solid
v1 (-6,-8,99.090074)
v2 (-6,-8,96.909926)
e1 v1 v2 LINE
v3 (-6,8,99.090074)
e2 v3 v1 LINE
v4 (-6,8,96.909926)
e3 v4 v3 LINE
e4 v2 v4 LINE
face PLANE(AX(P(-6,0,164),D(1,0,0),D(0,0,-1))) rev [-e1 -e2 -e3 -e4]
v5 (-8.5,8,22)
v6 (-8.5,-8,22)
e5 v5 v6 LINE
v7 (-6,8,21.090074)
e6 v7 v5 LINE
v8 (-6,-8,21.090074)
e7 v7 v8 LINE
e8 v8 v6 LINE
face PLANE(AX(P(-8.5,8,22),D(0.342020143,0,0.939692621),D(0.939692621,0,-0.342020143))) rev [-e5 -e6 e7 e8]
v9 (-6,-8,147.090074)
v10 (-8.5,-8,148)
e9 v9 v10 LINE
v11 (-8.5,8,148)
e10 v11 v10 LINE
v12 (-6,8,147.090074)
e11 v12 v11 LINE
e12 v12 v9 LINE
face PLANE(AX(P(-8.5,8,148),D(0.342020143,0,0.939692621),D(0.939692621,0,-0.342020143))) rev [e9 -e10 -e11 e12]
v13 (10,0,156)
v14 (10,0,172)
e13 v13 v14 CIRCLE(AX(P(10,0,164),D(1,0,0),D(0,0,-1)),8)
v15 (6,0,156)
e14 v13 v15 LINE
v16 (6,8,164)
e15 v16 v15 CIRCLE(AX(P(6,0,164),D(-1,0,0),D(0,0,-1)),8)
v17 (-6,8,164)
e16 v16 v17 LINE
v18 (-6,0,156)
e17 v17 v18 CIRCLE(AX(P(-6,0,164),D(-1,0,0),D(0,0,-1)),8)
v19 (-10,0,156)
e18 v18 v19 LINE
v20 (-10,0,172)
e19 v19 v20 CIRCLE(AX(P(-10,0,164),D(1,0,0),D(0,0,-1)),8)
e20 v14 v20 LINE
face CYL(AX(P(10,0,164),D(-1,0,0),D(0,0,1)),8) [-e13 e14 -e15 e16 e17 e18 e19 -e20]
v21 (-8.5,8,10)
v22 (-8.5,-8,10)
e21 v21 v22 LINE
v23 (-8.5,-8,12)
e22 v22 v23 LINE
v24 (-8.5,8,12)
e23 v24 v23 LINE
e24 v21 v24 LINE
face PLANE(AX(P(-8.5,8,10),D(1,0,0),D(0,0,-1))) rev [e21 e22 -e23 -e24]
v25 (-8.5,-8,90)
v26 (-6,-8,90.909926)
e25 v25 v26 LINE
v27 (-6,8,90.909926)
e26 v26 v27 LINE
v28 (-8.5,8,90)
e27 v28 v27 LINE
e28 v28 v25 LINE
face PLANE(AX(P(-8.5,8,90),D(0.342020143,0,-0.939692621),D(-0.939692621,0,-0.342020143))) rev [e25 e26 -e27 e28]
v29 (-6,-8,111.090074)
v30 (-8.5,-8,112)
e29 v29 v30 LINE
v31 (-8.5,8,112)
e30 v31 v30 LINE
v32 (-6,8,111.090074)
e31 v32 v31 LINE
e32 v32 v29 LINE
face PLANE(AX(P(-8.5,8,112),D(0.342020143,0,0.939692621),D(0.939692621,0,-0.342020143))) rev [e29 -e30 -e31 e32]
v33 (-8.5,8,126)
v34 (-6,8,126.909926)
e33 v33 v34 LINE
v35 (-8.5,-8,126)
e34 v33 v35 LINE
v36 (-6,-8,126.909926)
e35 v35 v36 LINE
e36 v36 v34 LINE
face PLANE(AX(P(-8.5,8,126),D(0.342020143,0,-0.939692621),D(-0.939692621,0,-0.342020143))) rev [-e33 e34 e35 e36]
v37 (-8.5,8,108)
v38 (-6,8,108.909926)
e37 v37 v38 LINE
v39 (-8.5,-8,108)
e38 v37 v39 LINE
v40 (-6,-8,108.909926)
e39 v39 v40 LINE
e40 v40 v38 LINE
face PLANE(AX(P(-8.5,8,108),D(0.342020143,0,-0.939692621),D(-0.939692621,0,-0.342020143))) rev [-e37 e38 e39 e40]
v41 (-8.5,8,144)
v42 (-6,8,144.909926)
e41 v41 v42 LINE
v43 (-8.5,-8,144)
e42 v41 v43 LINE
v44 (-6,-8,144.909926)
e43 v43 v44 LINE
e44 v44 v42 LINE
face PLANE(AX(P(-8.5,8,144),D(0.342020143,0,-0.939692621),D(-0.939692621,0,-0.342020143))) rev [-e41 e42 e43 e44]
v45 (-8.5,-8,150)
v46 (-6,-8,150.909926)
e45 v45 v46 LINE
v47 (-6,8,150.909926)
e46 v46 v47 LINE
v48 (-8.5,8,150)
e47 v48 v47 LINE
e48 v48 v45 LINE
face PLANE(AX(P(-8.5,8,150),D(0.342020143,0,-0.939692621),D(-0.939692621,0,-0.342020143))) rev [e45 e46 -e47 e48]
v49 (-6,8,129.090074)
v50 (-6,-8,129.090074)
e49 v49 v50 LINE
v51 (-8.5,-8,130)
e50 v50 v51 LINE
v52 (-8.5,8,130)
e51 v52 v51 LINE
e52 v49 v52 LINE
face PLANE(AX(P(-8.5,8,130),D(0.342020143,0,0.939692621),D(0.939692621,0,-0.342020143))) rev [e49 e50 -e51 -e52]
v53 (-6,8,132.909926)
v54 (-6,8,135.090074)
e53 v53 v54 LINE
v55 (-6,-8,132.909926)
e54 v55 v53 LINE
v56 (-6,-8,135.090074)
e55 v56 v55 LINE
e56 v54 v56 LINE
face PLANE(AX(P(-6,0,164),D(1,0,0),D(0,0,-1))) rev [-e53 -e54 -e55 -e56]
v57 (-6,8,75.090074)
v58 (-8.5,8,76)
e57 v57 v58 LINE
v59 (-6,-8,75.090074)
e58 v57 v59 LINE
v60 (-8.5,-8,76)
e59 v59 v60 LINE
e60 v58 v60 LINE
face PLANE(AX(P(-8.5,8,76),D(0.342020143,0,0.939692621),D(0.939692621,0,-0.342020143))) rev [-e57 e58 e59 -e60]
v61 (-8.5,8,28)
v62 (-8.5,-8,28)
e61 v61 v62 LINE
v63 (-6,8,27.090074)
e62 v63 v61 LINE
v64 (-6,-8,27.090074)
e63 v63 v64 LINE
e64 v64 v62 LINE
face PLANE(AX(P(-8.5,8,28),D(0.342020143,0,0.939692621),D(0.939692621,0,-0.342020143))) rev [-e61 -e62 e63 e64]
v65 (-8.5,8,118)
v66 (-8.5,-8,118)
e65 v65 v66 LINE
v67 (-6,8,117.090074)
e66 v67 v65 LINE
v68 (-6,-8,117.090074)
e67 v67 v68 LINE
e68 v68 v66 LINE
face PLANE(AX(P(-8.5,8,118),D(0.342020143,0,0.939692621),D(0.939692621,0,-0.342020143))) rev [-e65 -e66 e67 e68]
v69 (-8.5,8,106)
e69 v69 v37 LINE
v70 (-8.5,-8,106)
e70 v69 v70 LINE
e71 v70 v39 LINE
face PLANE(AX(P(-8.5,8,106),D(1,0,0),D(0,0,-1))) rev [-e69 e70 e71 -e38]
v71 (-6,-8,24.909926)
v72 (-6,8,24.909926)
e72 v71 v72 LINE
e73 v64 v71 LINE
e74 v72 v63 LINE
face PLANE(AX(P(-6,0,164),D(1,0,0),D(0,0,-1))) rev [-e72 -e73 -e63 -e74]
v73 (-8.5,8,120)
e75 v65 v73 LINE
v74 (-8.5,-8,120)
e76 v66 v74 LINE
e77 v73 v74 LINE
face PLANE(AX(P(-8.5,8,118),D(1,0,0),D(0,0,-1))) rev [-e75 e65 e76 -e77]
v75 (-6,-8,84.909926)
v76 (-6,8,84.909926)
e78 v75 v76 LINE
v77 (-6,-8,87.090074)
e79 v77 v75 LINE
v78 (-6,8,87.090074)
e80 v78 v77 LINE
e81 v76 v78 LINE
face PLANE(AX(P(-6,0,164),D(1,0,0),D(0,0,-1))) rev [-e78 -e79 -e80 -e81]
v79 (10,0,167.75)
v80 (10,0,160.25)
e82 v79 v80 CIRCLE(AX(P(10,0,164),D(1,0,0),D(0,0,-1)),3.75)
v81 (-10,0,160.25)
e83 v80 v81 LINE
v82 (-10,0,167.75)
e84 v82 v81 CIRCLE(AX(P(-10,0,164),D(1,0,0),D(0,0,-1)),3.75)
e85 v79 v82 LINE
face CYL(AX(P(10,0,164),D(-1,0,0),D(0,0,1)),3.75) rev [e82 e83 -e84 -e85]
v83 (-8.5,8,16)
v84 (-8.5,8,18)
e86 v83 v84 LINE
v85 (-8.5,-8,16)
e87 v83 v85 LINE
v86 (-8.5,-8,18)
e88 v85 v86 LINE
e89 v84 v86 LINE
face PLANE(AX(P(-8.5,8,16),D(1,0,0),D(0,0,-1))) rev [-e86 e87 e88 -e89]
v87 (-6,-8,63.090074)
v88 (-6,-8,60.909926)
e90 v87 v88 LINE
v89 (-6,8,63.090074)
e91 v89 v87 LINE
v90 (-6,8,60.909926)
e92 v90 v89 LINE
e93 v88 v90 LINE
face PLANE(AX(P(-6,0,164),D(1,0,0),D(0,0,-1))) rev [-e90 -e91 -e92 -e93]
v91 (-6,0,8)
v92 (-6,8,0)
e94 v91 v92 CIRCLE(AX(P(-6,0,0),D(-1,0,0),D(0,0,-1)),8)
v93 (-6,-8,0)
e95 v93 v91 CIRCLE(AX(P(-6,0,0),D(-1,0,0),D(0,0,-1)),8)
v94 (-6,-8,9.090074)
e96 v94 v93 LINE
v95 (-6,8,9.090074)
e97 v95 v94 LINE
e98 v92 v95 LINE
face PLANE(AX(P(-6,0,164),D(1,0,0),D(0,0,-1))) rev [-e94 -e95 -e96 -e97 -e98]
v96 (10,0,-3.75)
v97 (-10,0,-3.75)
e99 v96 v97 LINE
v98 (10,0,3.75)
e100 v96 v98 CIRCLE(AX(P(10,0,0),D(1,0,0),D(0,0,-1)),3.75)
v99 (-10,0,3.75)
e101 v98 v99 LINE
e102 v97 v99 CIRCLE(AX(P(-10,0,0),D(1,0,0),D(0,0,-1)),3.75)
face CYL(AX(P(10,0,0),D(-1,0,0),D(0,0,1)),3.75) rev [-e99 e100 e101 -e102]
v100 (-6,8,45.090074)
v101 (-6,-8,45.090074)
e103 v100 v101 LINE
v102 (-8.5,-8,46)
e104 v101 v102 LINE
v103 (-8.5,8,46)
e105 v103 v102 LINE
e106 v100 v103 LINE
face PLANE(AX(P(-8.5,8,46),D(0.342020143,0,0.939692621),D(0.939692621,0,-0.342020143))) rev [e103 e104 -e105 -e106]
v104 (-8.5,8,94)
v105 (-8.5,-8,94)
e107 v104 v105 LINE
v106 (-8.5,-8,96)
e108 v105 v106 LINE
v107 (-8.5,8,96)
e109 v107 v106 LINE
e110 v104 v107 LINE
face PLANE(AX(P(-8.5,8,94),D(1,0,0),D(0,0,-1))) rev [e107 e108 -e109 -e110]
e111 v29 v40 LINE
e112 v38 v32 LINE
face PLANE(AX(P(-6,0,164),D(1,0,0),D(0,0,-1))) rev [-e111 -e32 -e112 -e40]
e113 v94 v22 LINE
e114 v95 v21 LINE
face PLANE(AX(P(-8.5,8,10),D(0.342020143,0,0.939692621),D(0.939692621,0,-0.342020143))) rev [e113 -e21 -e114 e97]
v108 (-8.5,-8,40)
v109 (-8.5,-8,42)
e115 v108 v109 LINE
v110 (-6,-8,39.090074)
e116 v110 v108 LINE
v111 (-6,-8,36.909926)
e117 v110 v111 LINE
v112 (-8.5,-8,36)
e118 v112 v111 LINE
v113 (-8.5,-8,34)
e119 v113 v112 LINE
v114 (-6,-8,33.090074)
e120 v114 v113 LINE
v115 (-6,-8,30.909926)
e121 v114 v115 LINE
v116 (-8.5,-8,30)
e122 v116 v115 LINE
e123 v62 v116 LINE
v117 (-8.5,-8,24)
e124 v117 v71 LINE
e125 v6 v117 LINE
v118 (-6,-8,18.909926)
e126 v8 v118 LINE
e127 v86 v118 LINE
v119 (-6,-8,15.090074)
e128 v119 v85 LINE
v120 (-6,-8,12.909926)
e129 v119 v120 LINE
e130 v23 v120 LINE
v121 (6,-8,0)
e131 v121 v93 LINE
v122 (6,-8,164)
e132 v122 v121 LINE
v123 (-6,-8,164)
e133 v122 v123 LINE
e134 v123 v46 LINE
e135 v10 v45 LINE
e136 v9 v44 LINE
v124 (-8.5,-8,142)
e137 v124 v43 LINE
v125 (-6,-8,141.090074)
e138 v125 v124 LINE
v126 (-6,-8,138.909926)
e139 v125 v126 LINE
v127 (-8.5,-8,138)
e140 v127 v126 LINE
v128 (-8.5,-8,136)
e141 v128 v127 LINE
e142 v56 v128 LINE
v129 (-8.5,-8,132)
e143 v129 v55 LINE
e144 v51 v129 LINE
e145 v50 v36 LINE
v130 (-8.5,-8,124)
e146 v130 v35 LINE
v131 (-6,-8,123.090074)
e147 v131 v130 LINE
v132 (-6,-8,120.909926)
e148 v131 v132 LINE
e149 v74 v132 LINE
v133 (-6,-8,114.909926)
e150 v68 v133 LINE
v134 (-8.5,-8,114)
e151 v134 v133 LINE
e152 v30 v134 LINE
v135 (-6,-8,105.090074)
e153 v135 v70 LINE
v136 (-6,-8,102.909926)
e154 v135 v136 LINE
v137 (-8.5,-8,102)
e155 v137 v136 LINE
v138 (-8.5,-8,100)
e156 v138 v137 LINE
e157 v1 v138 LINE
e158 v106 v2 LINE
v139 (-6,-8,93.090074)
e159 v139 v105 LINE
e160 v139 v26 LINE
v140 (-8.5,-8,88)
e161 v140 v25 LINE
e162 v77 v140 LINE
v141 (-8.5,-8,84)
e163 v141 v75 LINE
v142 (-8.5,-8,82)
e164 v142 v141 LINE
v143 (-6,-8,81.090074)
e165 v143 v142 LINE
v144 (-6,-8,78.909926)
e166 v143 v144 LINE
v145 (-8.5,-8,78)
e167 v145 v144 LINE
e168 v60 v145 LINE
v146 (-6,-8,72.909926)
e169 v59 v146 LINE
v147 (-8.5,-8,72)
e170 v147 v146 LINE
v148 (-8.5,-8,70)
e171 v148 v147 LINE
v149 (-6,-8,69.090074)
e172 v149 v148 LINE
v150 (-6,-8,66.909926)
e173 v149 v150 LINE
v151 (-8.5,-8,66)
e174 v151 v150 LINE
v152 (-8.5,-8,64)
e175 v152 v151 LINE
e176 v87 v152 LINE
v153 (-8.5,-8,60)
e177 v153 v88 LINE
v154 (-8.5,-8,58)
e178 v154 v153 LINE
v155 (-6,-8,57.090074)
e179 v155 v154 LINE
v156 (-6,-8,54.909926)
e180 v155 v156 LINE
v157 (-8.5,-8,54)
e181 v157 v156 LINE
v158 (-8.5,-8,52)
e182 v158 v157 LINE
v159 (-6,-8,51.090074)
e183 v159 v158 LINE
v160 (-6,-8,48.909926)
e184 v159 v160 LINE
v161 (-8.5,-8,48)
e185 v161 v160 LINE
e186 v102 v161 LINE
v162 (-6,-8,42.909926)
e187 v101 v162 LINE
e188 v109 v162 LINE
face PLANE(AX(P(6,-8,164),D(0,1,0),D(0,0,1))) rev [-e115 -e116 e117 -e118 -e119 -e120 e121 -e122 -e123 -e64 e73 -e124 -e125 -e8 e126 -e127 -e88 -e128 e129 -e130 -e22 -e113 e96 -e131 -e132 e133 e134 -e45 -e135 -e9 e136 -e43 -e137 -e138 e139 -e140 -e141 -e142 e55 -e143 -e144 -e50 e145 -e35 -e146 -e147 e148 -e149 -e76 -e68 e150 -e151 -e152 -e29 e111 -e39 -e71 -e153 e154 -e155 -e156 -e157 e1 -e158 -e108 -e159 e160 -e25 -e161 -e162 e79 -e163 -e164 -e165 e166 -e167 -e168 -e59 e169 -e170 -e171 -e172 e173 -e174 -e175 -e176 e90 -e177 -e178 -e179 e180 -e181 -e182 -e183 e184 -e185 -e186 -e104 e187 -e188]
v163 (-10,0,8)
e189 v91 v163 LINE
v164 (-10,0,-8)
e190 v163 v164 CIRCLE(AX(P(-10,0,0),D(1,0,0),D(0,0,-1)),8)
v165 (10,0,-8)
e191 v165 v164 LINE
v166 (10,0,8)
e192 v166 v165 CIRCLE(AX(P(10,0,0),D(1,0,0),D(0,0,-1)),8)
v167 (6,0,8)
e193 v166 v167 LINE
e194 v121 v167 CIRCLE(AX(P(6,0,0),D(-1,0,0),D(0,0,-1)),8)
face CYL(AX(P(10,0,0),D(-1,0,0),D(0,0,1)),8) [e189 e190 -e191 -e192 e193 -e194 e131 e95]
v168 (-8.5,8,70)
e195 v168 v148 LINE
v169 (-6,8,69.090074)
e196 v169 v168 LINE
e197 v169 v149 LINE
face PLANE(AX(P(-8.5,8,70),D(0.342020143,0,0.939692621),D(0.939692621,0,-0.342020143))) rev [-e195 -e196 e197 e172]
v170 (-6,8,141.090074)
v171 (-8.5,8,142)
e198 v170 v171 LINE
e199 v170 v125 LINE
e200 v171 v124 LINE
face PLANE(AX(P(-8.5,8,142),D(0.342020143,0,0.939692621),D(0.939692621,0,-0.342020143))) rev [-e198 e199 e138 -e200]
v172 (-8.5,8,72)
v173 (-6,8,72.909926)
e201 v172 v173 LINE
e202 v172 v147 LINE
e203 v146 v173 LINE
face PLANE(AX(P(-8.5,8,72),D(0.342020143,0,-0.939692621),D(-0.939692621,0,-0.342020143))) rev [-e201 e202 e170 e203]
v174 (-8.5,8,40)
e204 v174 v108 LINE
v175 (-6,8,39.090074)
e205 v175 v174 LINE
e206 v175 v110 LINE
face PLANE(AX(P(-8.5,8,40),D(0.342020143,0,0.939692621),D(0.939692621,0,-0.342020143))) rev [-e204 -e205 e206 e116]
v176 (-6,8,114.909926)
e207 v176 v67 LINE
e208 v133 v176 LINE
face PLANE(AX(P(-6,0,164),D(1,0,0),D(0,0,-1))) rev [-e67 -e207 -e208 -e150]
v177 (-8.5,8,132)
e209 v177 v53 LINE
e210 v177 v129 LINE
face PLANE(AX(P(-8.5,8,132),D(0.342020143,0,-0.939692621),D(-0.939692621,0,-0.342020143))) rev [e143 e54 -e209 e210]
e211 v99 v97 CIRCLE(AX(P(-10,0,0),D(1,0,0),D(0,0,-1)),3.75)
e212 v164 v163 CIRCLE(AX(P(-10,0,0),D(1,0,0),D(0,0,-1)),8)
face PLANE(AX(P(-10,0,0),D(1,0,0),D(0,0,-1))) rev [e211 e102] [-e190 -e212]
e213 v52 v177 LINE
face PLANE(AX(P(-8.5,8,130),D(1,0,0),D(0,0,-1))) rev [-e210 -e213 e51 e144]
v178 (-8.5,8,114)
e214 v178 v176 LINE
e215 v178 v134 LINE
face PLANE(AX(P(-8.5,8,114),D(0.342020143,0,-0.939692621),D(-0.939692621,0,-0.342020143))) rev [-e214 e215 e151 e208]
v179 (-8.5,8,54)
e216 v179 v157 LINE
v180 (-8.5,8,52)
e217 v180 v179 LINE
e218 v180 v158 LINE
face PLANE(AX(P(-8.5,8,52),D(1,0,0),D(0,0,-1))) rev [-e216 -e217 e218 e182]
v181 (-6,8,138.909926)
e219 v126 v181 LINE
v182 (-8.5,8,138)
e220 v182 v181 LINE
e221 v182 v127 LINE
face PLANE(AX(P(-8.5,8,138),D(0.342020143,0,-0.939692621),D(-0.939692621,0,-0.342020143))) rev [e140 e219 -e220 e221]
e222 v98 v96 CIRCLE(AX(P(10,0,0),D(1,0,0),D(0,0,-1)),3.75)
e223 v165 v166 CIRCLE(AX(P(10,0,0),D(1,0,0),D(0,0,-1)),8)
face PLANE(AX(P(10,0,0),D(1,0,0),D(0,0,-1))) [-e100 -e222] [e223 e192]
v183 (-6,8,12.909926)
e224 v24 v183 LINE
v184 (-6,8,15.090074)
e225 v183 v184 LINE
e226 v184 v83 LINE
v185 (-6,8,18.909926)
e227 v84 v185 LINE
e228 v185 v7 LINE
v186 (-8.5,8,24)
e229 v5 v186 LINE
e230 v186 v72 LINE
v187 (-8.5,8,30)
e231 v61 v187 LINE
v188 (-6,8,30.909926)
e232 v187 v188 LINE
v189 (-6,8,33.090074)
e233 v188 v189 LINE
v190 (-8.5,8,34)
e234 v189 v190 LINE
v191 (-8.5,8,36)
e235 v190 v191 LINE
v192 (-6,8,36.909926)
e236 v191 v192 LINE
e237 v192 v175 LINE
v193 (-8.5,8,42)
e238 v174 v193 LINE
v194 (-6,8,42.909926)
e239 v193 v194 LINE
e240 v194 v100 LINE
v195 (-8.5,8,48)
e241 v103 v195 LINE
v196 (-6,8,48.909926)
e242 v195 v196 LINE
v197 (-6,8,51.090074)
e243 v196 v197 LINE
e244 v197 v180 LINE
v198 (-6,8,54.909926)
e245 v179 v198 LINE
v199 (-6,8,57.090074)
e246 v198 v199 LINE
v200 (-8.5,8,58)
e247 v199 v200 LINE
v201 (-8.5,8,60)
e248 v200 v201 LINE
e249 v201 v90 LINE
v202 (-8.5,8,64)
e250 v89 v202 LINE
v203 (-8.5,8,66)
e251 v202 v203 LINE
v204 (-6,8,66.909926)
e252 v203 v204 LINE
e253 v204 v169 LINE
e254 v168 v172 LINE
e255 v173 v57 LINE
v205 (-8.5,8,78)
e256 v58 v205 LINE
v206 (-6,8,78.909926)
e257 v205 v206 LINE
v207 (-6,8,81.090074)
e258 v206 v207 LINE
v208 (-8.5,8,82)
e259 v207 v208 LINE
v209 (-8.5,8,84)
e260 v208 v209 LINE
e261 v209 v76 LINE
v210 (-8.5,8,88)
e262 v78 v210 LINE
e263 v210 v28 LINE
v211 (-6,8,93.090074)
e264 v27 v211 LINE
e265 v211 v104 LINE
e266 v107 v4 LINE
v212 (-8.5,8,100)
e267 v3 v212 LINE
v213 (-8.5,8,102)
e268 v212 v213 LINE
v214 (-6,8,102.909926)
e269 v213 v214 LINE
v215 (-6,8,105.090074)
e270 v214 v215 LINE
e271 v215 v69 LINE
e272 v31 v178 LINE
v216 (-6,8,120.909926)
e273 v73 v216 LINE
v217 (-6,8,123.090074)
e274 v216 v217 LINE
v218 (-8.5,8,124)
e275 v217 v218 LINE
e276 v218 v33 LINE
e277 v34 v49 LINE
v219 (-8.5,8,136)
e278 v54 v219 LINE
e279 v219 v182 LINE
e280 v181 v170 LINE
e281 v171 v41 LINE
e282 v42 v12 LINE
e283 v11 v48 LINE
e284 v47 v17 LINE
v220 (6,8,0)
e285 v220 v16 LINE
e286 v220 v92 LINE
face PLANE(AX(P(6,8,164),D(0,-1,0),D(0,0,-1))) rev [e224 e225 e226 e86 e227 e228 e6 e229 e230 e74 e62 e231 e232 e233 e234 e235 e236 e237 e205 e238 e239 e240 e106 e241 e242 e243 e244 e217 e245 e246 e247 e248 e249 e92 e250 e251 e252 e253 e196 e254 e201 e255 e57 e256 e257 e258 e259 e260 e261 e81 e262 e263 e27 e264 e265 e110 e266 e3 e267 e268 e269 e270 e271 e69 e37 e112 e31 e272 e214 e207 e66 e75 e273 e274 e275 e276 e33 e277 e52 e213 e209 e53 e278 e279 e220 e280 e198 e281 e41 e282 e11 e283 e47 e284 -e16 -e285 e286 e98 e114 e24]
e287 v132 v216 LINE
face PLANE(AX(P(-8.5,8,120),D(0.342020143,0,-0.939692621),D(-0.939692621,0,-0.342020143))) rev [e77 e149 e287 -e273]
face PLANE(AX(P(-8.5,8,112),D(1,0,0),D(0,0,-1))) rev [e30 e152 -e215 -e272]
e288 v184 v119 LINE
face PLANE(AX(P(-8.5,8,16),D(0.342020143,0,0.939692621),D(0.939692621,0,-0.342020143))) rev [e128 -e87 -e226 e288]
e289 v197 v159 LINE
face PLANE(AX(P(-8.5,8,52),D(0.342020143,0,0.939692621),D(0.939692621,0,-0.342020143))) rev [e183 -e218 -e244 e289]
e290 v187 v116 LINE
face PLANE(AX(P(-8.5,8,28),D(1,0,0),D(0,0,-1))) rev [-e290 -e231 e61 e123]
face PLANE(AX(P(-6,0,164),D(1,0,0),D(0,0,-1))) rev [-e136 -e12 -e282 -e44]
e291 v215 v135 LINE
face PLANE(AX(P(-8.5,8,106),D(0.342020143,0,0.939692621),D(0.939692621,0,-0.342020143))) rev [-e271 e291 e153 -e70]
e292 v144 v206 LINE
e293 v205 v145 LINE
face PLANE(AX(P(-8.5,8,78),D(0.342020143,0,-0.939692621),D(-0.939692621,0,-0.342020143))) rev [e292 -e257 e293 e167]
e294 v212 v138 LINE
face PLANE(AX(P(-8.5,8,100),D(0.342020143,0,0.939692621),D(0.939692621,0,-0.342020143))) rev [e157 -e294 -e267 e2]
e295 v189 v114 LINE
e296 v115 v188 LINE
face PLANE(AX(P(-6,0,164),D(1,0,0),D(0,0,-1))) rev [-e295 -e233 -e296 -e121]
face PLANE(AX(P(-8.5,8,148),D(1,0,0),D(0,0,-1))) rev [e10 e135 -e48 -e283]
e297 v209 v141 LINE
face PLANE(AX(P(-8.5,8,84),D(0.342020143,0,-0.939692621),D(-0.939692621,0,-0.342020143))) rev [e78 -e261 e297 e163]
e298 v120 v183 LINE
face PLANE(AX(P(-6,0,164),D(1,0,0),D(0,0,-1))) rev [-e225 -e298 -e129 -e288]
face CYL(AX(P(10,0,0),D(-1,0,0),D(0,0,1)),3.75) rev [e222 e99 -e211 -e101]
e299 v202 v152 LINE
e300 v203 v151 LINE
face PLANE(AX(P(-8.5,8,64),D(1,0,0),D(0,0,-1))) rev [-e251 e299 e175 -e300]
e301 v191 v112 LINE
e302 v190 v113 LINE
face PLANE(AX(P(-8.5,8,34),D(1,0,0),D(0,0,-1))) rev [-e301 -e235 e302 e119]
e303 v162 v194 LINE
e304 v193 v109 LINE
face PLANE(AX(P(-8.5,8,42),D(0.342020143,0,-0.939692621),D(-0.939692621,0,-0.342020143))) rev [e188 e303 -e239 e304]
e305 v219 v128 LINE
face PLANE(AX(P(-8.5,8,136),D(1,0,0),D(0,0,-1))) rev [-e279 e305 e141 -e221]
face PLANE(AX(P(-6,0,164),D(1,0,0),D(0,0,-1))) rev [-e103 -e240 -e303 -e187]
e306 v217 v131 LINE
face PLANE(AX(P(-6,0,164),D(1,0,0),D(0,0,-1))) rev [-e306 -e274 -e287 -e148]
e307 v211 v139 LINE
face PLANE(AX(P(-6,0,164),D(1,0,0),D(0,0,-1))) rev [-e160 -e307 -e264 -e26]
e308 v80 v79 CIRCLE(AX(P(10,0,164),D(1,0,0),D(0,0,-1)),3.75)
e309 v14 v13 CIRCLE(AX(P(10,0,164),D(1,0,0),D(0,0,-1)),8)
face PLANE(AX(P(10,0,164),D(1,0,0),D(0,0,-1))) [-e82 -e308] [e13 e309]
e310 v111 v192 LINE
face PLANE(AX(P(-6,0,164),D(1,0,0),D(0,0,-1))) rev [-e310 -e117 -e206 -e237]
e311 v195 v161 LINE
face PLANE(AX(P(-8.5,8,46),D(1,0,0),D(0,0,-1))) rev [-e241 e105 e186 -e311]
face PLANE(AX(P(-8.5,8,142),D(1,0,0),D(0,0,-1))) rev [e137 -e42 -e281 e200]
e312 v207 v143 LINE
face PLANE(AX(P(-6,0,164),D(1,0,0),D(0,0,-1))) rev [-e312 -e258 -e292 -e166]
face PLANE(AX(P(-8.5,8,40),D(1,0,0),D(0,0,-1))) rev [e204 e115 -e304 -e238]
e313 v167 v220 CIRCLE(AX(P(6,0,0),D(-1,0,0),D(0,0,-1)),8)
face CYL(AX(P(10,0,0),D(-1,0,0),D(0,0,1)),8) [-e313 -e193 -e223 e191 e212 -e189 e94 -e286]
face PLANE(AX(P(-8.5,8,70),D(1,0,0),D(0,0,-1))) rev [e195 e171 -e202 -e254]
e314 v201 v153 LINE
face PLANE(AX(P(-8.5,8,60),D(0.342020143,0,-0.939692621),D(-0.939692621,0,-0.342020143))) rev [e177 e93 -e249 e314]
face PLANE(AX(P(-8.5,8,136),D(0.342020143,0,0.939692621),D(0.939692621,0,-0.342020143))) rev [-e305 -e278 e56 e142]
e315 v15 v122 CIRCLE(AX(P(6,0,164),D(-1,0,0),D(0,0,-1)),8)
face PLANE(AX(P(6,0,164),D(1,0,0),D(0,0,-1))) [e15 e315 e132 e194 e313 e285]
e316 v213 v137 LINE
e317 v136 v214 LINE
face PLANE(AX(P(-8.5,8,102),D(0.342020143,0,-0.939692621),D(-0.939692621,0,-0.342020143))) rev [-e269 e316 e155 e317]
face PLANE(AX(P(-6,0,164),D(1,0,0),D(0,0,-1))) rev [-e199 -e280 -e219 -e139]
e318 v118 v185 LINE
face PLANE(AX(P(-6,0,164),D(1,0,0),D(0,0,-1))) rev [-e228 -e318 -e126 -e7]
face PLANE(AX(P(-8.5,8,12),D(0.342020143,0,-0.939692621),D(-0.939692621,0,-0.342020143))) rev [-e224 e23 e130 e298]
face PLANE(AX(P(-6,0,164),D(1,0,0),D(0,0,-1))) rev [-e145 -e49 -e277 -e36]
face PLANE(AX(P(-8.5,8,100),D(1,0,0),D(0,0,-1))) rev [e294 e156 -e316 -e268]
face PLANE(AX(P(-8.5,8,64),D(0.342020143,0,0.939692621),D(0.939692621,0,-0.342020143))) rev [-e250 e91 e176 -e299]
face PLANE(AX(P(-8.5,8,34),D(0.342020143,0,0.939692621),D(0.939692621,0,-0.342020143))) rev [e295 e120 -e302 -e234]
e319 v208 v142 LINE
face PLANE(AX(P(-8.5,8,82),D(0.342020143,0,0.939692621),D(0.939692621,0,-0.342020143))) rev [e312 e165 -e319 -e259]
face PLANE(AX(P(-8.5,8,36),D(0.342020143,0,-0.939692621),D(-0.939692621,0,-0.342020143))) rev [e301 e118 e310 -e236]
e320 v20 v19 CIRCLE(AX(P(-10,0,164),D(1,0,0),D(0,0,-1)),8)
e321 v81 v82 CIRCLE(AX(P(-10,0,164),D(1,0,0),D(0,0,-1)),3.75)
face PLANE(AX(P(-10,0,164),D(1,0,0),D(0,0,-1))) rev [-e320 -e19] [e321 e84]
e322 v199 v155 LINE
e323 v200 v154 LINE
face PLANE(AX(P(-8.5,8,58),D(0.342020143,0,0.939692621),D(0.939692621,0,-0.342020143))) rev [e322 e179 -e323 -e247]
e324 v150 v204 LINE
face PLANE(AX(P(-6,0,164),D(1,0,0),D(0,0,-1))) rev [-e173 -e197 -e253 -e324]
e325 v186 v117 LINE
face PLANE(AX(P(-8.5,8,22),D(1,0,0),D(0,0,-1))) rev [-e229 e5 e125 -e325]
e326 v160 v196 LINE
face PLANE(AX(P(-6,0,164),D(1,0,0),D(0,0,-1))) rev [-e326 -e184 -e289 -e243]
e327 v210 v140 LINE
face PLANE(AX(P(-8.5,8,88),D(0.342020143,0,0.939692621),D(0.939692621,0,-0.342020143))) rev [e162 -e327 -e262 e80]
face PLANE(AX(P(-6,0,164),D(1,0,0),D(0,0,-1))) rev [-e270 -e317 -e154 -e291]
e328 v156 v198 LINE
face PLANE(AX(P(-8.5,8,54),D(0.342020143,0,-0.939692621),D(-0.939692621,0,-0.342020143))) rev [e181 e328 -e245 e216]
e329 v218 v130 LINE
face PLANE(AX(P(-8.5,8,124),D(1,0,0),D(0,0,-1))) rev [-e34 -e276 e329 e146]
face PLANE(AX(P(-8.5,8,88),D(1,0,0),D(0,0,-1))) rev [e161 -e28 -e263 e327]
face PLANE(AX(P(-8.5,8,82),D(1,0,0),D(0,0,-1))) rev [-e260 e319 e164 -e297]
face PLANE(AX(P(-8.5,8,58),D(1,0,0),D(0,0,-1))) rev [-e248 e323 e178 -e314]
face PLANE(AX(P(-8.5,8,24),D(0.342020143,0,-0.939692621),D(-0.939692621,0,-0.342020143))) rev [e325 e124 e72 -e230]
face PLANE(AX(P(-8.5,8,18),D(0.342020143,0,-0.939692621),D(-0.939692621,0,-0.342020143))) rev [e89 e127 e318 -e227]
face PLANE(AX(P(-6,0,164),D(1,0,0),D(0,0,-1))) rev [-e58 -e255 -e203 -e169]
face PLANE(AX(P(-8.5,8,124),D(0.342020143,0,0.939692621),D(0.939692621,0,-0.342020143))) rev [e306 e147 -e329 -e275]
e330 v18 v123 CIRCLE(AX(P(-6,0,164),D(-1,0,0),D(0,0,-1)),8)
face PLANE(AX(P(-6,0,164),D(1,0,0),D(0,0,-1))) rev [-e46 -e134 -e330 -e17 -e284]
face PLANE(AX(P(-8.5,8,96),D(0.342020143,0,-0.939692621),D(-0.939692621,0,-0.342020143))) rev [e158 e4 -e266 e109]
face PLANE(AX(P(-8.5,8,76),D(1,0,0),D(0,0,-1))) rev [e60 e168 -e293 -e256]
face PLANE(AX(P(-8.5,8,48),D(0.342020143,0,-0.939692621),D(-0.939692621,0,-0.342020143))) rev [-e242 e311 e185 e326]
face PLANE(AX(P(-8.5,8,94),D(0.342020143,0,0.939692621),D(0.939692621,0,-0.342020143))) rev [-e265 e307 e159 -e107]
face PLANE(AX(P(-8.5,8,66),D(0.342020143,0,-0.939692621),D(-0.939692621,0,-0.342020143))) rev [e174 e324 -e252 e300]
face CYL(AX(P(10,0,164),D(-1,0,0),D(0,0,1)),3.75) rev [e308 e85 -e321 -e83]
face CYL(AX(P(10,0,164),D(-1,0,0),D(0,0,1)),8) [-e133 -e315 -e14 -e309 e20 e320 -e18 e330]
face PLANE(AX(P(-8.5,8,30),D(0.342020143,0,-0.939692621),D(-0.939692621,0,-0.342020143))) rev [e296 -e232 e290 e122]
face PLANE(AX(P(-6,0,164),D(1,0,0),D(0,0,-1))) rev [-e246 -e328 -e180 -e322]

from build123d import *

# Parameters (mm, degrees)
EYE_BAR_PROFILE_SKETCH_R   = 8
EYE_BAR_PROFILE_SKETCH_R_2 = 3.75
BAR_WITH_EYE_ENDS_DEPTH    = 10
BAR_WITH_EYE_ENDS_2_DEPTH  = 10
RACK_BODY_DEPTH            = 6
RACK_TEETH_24X_DEPTH       = 8


with BuildPart() as part:
    # Eye Bar Profile Sketch → Bar With Eye Ends (new, symmetric)
    with BuildSketch(Plane(origin=(0, 0, 0), x_dir=(0, 0, -1), z_dir=(1, 0, 0))):
        Circle(EYE_BAR_PROFILE_SKETCH_R)
        Circle(EYE_BAR_PROFILE_SKETCH_R_2, mode=Mode.SUBTRACT)
    extrude(amount=BAR_WITH_EYE_ENDS_DEPTH, both=True)



with BuildPart() as body_2:
    # Eye Bar Profile Sketch → Bar With Eye Ends 2 (new, symmetric)
    with BuildSketch(Plane(origin=(0, 0, 0), x_dir=(0, 0, -1), z_dir=(1, 0, 0))):
        with Locations((-164, 0)):
            Circle(EYE_BAR_PROFILE_SKETCH_R)
        with Locations((-164, 0)):
            Circle(EYE_BAR_PROFILE_SKETCH_R_2, mode=Mode.SUBTRACT)
    extrude(amount=BAR_WITH_EYE_ENDS_2_DEPTH, both=True)


with BuildPart() as part_1:
    add(part.part)

    add(body_2.part)  # Rack Body merges body 2
    # Rack Body Sketch → Rack Body (add, symmetric)
    with BuildSketch(Plane(origin=(0, 0, 0), x_dir=(0, 0, -1), z_dir=(1, 0, 0))):
        with BuildLine():
            Line((-164, 8), (0, 8))
            ThreePointArc((0, 8), (-8, 0), (0, -8))
            Line((0, -8), (-164, -8))
            ThreePointArc((-164, -8), (-156, 0), (-164, 8))
        make_face()
    extrude(amount=RACK_BODY_DEPTH, both=True)

    # Rack Teeth Profile Sketch → Rack Teeth 24x (add, symmetric)
    with BuildSketch(Plane(origin=(0, 0, 0), x_dir=(1, 0, 0), z_dir=(0, 1, 0))):
        Polygon((-8.5, -10), (-8.5, -12), (-5.490653606, -13.095312512), (-5.490653606, -8.904687488), align=None)
        Polygon((-8.5, -16), (-5.490653606, -14.904687488), (-5.490653606, -19.095312512), (-8.5, -18), align=None)
        Polygon((-8.5, -22), (-5.490653606, -20.904687488), (-5.490653606, -25.095312512), (-8.5, -24), align=None)
        Polygon((-8.5, -28), (-5.490653606, -26.904687488), (-5.490653606, -31.095312512), (-8.5, -30), align=None)
        Polygon((-8.5, -34), (-5.490653606, -32.904687488), (-5.490653606, -37.095312512), (-8.5, -36), align=None)
        Polygon((-8.5, -40), (-5.490653606, -38.904687488), (-5.490653606, -43.095312512), (-8.5, -42), align=None)
        Polygon((-8.5, -46), (-5.490653606, -44.904687488), (-5.490653606, -49.095312512), (-8.5, -48), align=None)
        Polygon((-8.5, -52), (-5.490653606, -50.904687488), (-5.490653606, -55.095312512), (-8.5, -54), align=None)
        Polygon((-8.5, -58), (-5.490653606, -56.904687488), (-5.490653606, -61.095312512), (-8.5, -60), align=None)
        Polygon((-8.5, -64), (-5.490653606, -62.904687488), (-5.490653606, -67.095312512), (-8.5, -66), align=None)
        Polygon((-8.5, -70), (-5.490653606, -68.904687488), (-5.490653606, -73.095312512), (-8.5, -72), align=None)
        Polygon((-8.5, -76), (-5.490653606, -74.904687488), (-5.490653606, -79.095312512), (-8.5, -78), align=None)
        Polygon((-8.5, -82), (-5.490653606, -80.904687488), (-5.490653606, -85.095312512), (-8.5, -84), align=None)
        Polygon((-8.5, -88), (-5.490653606, -86.904687488), (-5.490653606, -91.095312512), (-8.5, -90), align=None)
        Polygon((-8.5, -94), (-5.490653606, -92.904687488), (-5.490653606, -97.095312512), (-8.5, -96), align=None)
        Polygon((-8.5, -100), (-5.490653606, -98.904687488), (-5.490653606, -103.095312512), (-8.5, -102), align=None)
        Polygon((-8.5, -106), (-5.490653606, -104.904687488), (-5.490653606, -109.095312512), (-8.5, -108), align=None)
        Polygon((-8.5, -112), (-5.490653606, -110.904687488), (-5.490653606, -115.095312512), (-8.5, -114), align=None)
        Polygon((-8.5, -118), (-5.490653606, -116.904687488), (-5.490653606, -121.095312512), (-8.5, -120), align=None)
        Polygon((-8.5, -124), (-5.490653606, -122.904687488), (-5.490653606, -127.095312512), (-8.5, -126), align=None)
        Polygon((-8.5, -130), (-5.490653606, -128.904687488), (-5.490653606, -133.095312512), (-8.5, -132), align=None)
        Polygon((-8.5, -136), (-5.490653606, -134.904687488), (-5.490653606, -139.095312512), (-8.5, -138), align=None)
        Polygon((-8.5, -142), (-5.490653606, -140.904687488), (-5.490653606, -145.095312512), (-8.5, -144), align=None)
        Polygon((-8.5, -148), (-5.490653606, -146.904687488), (-5.490653606, -151.095312512), (-8.5, -150), align=None)
    extrude(amount=RACK_TEETH_24X_DEPTH, both=True)


solid = part_1.part
